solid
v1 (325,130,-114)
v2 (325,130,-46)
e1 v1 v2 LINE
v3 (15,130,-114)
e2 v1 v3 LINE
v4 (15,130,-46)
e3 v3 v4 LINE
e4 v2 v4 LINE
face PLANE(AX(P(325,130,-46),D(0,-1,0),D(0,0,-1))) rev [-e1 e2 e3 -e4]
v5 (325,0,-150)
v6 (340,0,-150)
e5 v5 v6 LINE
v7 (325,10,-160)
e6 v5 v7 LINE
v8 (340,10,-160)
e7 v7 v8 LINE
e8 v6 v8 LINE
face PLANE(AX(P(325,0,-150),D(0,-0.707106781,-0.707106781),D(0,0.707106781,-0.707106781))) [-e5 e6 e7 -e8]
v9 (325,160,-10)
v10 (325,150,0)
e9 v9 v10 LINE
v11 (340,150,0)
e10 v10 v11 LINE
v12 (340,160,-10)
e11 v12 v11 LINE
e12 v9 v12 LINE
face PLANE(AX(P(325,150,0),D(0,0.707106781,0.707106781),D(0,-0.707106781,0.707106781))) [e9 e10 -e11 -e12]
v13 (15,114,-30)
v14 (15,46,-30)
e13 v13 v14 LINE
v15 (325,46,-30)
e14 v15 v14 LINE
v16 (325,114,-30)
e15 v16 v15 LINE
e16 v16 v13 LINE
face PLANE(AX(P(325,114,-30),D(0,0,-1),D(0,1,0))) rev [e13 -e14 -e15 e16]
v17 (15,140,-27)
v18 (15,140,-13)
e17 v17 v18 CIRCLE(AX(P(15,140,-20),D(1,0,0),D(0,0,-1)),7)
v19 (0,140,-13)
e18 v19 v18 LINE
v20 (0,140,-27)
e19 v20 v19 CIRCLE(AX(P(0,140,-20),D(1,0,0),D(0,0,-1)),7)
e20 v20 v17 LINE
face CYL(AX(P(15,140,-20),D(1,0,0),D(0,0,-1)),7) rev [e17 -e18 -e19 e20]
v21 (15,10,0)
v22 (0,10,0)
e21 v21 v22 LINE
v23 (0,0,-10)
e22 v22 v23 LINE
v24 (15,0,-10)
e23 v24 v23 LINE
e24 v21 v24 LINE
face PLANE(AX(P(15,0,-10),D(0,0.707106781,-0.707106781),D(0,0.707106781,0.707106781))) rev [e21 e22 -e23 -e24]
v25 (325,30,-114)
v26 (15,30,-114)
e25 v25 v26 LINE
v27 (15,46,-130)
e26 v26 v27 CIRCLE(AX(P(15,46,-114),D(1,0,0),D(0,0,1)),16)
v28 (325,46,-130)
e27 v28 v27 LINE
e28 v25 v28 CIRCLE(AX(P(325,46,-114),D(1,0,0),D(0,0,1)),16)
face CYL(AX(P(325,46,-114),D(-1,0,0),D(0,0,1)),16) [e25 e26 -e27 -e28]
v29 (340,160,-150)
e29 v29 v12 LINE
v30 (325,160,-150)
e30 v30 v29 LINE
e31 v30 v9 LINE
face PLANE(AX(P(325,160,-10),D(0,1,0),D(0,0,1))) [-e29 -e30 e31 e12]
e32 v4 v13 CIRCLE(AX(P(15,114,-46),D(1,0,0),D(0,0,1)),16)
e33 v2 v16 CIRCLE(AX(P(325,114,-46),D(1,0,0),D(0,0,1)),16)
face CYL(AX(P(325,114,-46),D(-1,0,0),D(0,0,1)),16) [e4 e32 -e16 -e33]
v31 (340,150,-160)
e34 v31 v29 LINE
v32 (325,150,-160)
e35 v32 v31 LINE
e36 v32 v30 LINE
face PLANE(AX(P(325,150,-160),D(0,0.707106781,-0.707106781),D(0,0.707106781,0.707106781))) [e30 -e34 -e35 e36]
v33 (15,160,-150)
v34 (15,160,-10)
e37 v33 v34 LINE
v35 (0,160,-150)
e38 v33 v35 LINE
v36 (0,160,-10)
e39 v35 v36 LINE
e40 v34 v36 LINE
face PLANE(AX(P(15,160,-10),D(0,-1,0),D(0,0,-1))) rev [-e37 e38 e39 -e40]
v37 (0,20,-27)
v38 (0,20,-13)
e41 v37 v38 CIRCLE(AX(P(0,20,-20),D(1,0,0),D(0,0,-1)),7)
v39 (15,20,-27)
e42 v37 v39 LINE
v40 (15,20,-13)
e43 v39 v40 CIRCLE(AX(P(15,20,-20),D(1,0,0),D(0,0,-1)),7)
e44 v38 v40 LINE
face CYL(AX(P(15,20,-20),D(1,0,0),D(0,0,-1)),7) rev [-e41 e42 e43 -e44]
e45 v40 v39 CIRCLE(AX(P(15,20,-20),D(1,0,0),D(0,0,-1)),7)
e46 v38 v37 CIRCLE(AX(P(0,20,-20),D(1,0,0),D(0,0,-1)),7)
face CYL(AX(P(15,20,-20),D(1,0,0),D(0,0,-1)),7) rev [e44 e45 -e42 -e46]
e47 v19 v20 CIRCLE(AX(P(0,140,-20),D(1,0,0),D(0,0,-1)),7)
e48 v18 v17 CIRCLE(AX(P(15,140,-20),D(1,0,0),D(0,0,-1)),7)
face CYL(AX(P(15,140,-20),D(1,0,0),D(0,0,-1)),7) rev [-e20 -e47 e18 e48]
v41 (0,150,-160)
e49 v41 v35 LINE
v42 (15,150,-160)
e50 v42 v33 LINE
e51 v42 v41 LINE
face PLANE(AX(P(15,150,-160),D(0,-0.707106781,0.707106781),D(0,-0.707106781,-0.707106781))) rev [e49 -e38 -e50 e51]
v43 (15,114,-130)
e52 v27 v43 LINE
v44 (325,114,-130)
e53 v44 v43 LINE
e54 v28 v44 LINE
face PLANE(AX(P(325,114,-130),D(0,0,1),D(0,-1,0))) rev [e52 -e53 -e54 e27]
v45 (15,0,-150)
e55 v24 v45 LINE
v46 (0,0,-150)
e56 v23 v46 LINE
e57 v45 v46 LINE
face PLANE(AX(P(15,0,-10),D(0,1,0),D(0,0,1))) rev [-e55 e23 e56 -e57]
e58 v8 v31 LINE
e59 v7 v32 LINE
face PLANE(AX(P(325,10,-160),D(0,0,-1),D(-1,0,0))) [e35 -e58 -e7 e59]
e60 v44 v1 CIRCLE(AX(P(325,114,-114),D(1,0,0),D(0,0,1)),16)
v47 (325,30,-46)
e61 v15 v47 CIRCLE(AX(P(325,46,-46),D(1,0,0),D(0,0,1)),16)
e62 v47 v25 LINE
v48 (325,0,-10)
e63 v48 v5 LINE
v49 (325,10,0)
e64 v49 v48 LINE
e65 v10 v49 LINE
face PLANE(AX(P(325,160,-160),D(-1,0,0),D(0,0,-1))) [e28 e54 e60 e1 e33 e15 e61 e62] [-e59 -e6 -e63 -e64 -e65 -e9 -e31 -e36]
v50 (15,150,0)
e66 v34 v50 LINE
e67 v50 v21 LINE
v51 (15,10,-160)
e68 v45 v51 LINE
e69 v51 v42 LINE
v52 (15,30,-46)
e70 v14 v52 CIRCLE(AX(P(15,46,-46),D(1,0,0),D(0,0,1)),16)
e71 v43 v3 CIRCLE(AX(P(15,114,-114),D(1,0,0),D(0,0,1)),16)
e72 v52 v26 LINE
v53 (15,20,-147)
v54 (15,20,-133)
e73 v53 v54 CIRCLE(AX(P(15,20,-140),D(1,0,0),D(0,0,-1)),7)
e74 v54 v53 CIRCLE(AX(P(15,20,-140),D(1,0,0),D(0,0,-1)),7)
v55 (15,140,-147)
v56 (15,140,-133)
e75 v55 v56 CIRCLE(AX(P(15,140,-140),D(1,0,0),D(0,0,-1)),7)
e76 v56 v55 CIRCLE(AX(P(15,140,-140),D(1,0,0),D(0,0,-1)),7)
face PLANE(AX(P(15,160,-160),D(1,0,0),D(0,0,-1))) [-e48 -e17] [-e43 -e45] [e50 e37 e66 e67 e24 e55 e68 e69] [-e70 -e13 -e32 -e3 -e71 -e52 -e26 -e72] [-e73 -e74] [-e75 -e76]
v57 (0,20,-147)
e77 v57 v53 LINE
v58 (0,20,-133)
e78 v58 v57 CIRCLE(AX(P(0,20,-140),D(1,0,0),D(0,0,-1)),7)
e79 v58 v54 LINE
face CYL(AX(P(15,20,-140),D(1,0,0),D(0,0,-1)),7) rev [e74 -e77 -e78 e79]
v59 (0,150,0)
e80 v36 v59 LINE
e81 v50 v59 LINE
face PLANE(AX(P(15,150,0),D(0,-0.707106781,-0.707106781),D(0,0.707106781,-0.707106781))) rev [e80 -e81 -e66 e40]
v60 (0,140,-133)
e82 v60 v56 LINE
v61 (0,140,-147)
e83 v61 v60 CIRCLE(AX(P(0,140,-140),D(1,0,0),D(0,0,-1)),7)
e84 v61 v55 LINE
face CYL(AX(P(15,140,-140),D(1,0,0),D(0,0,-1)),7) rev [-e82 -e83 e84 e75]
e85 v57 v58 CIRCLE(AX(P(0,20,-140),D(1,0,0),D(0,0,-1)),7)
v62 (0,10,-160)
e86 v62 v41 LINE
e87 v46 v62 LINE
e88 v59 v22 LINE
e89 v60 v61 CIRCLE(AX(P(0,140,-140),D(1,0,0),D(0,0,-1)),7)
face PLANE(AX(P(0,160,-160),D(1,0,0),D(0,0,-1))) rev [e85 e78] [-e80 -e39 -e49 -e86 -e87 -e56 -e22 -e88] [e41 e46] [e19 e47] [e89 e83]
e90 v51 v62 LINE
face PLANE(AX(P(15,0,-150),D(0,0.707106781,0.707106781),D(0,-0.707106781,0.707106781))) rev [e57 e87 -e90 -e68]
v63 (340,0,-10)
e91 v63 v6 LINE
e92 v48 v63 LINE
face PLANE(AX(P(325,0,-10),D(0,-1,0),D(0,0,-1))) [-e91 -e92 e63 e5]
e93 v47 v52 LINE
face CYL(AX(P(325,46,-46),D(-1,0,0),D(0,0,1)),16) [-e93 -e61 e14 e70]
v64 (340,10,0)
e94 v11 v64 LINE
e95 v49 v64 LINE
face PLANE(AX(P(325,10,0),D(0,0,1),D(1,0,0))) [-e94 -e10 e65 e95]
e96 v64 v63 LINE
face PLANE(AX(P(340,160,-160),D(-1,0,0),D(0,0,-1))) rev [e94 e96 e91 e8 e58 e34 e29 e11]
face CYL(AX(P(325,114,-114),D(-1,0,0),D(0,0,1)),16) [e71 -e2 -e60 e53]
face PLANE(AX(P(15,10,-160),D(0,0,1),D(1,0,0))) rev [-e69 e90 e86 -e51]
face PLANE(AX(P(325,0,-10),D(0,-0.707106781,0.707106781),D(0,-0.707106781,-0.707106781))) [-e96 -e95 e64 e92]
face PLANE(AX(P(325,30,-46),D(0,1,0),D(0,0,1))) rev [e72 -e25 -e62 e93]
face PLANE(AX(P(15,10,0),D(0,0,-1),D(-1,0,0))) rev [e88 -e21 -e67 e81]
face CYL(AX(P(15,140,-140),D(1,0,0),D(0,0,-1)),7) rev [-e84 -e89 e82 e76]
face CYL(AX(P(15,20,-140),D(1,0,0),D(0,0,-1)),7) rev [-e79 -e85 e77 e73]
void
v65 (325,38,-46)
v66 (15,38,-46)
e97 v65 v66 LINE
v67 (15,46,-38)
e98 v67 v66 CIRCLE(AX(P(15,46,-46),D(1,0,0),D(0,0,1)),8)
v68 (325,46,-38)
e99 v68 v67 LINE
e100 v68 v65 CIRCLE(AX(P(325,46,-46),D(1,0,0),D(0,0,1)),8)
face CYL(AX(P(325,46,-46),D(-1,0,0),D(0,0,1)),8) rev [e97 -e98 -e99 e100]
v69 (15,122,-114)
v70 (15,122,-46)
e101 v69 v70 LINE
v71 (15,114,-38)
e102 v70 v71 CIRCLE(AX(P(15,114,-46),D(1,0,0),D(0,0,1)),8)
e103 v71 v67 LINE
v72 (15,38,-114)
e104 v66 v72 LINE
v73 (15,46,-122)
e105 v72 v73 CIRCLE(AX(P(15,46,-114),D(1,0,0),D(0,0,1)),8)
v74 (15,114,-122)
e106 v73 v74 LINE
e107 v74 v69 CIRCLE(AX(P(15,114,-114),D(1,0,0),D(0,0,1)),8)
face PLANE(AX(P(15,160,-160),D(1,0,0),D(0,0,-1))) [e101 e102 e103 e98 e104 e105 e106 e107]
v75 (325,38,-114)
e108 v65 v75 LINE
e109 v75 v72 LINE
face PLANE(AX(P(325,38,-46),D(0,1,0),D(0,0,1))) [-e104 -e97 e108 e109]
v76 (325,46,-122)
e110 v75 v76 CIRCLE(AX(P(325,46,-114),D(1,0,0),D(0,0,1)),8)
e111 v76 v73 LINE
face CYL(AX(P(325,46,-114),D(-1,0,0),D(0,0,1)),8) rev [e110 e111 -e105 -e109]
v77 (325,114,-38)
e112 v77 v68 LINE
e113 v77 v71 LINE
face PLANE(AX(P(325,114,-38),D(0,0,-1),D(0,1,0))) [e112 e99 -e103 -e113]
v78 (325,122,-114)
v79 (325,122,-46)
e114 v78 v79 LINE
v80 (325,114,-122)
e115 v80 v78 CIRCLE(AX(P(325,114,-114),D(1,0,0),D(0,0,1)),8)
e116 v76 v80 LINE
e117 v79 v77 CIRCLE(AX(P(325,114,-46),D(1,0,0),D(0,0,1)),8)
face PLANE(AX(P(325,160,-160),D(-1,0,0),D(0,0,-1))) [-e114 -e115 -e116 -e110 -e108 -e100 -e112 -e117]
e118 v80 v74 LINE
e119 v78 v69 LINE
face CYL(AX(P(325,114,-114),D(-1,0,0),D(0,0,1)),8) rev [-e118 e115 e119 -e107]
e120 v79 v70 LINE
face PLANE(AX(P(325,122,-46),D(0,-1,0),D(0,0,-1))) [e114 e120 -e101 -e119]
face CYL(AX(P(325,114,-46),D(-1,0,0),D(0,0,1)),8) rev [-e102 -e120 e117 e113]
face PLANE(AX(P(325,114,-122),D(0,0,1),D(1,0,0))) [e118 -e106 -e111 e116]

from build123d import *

# Parameters (mm, degrees)
BOSS_EXTRUDE1_DEPTH            = 15
BOSS_EXTRUDE2_DEPTH            = 310
F_14_0_14_DIAMETER_HOLE1_D     = 14
F_14_0_14_DIAMETER_HOLE1_DEPTH = 15


with BuildPart() as part:
    # Sketch1 → Boss-Extrude1 (new body)
    with BuildSketch(Plane(origin=(0, 0, 0), x_dir=(0, 0, -1), z_dir=(1, 0, 0))):
        Polygon((0, 150), (10, 160), (150, 160), (160, 150), (160, 10), (150, 0), (10, 0), (0, 10), align=None)
    boss_extrude1 = extrude(amount=BOSS_EXTRUDE1_DEPTH)

    # Sketch2 → Boss-Extrude2 (add)
    with BuildSketch(Plane(origin=(15, 0, 0), x_dir=(0, 0, -1), z_dir=(1, 0, 0))):
        with BuildLine():
            Line((46, 130), (114, 130))
            ThreePointArc((114, 130), (125.313708499, 125.313708499), (130, 114))
            Line((130, 114), (130, 46))
            ThreePointArc((130, 46), (125.313708499, 34.686291501), (114, 30))
            Line((114, 30), (46, 30))
            ThreePointArc((46, 30), (34.686291501, 34.686291501), (30, 46))
            Line((30, 46), (30, 114))
            ThreePointArc((30, 114), (34.686291501, 125.313708499), (46, 130))
        make_face()
        with BuildLine():
            Line((46, 122), (114, 122))
            ThreePointArc((114, 122), (119.656854249, 119.656854249), (122, 114))
            Line((122, 114), (122, 46))
            ThreePointArc((122, 46), (119.656854249, 40.343145751), (114, 38))
            Line((114, 38), (46, 38))
            ThreePointArc((46, 38), (40.343145751, 40.343145751), (38, 46))
            Line((38, 46), (38, 114))
            ThreePointArc((38, 114), (40.343145751, 119.656854249), (46, 122))
        make_face(mode=Mode.SUBTRACT)
    extrude(amount=BOSS_EXTRUDE2_DEPTH)

    # Mirror1: Boss-Extrude1 across plane
    add(boss_extrude1.mirror(Plane(origin=(170, 0, 0), x_dir=(0, 0, 1), z_dir=(1, 0, 0))))

    # Ø14.0 (14) Diameter Hole1
    with Locations(Plane(origin=(15, 140, -140), x_dir=(0, 0, 1), z_dir=(1, 0, 0))):
        with Locations((0, 0), (0, 120), (120, 0), (120, 120)):
            Hole(F_14_0_14_DIAMETER_HOLE1_D / 2, depth=F_14_0_14_DIAMETER_HOLE1_DEPTH)


solid = part.part
